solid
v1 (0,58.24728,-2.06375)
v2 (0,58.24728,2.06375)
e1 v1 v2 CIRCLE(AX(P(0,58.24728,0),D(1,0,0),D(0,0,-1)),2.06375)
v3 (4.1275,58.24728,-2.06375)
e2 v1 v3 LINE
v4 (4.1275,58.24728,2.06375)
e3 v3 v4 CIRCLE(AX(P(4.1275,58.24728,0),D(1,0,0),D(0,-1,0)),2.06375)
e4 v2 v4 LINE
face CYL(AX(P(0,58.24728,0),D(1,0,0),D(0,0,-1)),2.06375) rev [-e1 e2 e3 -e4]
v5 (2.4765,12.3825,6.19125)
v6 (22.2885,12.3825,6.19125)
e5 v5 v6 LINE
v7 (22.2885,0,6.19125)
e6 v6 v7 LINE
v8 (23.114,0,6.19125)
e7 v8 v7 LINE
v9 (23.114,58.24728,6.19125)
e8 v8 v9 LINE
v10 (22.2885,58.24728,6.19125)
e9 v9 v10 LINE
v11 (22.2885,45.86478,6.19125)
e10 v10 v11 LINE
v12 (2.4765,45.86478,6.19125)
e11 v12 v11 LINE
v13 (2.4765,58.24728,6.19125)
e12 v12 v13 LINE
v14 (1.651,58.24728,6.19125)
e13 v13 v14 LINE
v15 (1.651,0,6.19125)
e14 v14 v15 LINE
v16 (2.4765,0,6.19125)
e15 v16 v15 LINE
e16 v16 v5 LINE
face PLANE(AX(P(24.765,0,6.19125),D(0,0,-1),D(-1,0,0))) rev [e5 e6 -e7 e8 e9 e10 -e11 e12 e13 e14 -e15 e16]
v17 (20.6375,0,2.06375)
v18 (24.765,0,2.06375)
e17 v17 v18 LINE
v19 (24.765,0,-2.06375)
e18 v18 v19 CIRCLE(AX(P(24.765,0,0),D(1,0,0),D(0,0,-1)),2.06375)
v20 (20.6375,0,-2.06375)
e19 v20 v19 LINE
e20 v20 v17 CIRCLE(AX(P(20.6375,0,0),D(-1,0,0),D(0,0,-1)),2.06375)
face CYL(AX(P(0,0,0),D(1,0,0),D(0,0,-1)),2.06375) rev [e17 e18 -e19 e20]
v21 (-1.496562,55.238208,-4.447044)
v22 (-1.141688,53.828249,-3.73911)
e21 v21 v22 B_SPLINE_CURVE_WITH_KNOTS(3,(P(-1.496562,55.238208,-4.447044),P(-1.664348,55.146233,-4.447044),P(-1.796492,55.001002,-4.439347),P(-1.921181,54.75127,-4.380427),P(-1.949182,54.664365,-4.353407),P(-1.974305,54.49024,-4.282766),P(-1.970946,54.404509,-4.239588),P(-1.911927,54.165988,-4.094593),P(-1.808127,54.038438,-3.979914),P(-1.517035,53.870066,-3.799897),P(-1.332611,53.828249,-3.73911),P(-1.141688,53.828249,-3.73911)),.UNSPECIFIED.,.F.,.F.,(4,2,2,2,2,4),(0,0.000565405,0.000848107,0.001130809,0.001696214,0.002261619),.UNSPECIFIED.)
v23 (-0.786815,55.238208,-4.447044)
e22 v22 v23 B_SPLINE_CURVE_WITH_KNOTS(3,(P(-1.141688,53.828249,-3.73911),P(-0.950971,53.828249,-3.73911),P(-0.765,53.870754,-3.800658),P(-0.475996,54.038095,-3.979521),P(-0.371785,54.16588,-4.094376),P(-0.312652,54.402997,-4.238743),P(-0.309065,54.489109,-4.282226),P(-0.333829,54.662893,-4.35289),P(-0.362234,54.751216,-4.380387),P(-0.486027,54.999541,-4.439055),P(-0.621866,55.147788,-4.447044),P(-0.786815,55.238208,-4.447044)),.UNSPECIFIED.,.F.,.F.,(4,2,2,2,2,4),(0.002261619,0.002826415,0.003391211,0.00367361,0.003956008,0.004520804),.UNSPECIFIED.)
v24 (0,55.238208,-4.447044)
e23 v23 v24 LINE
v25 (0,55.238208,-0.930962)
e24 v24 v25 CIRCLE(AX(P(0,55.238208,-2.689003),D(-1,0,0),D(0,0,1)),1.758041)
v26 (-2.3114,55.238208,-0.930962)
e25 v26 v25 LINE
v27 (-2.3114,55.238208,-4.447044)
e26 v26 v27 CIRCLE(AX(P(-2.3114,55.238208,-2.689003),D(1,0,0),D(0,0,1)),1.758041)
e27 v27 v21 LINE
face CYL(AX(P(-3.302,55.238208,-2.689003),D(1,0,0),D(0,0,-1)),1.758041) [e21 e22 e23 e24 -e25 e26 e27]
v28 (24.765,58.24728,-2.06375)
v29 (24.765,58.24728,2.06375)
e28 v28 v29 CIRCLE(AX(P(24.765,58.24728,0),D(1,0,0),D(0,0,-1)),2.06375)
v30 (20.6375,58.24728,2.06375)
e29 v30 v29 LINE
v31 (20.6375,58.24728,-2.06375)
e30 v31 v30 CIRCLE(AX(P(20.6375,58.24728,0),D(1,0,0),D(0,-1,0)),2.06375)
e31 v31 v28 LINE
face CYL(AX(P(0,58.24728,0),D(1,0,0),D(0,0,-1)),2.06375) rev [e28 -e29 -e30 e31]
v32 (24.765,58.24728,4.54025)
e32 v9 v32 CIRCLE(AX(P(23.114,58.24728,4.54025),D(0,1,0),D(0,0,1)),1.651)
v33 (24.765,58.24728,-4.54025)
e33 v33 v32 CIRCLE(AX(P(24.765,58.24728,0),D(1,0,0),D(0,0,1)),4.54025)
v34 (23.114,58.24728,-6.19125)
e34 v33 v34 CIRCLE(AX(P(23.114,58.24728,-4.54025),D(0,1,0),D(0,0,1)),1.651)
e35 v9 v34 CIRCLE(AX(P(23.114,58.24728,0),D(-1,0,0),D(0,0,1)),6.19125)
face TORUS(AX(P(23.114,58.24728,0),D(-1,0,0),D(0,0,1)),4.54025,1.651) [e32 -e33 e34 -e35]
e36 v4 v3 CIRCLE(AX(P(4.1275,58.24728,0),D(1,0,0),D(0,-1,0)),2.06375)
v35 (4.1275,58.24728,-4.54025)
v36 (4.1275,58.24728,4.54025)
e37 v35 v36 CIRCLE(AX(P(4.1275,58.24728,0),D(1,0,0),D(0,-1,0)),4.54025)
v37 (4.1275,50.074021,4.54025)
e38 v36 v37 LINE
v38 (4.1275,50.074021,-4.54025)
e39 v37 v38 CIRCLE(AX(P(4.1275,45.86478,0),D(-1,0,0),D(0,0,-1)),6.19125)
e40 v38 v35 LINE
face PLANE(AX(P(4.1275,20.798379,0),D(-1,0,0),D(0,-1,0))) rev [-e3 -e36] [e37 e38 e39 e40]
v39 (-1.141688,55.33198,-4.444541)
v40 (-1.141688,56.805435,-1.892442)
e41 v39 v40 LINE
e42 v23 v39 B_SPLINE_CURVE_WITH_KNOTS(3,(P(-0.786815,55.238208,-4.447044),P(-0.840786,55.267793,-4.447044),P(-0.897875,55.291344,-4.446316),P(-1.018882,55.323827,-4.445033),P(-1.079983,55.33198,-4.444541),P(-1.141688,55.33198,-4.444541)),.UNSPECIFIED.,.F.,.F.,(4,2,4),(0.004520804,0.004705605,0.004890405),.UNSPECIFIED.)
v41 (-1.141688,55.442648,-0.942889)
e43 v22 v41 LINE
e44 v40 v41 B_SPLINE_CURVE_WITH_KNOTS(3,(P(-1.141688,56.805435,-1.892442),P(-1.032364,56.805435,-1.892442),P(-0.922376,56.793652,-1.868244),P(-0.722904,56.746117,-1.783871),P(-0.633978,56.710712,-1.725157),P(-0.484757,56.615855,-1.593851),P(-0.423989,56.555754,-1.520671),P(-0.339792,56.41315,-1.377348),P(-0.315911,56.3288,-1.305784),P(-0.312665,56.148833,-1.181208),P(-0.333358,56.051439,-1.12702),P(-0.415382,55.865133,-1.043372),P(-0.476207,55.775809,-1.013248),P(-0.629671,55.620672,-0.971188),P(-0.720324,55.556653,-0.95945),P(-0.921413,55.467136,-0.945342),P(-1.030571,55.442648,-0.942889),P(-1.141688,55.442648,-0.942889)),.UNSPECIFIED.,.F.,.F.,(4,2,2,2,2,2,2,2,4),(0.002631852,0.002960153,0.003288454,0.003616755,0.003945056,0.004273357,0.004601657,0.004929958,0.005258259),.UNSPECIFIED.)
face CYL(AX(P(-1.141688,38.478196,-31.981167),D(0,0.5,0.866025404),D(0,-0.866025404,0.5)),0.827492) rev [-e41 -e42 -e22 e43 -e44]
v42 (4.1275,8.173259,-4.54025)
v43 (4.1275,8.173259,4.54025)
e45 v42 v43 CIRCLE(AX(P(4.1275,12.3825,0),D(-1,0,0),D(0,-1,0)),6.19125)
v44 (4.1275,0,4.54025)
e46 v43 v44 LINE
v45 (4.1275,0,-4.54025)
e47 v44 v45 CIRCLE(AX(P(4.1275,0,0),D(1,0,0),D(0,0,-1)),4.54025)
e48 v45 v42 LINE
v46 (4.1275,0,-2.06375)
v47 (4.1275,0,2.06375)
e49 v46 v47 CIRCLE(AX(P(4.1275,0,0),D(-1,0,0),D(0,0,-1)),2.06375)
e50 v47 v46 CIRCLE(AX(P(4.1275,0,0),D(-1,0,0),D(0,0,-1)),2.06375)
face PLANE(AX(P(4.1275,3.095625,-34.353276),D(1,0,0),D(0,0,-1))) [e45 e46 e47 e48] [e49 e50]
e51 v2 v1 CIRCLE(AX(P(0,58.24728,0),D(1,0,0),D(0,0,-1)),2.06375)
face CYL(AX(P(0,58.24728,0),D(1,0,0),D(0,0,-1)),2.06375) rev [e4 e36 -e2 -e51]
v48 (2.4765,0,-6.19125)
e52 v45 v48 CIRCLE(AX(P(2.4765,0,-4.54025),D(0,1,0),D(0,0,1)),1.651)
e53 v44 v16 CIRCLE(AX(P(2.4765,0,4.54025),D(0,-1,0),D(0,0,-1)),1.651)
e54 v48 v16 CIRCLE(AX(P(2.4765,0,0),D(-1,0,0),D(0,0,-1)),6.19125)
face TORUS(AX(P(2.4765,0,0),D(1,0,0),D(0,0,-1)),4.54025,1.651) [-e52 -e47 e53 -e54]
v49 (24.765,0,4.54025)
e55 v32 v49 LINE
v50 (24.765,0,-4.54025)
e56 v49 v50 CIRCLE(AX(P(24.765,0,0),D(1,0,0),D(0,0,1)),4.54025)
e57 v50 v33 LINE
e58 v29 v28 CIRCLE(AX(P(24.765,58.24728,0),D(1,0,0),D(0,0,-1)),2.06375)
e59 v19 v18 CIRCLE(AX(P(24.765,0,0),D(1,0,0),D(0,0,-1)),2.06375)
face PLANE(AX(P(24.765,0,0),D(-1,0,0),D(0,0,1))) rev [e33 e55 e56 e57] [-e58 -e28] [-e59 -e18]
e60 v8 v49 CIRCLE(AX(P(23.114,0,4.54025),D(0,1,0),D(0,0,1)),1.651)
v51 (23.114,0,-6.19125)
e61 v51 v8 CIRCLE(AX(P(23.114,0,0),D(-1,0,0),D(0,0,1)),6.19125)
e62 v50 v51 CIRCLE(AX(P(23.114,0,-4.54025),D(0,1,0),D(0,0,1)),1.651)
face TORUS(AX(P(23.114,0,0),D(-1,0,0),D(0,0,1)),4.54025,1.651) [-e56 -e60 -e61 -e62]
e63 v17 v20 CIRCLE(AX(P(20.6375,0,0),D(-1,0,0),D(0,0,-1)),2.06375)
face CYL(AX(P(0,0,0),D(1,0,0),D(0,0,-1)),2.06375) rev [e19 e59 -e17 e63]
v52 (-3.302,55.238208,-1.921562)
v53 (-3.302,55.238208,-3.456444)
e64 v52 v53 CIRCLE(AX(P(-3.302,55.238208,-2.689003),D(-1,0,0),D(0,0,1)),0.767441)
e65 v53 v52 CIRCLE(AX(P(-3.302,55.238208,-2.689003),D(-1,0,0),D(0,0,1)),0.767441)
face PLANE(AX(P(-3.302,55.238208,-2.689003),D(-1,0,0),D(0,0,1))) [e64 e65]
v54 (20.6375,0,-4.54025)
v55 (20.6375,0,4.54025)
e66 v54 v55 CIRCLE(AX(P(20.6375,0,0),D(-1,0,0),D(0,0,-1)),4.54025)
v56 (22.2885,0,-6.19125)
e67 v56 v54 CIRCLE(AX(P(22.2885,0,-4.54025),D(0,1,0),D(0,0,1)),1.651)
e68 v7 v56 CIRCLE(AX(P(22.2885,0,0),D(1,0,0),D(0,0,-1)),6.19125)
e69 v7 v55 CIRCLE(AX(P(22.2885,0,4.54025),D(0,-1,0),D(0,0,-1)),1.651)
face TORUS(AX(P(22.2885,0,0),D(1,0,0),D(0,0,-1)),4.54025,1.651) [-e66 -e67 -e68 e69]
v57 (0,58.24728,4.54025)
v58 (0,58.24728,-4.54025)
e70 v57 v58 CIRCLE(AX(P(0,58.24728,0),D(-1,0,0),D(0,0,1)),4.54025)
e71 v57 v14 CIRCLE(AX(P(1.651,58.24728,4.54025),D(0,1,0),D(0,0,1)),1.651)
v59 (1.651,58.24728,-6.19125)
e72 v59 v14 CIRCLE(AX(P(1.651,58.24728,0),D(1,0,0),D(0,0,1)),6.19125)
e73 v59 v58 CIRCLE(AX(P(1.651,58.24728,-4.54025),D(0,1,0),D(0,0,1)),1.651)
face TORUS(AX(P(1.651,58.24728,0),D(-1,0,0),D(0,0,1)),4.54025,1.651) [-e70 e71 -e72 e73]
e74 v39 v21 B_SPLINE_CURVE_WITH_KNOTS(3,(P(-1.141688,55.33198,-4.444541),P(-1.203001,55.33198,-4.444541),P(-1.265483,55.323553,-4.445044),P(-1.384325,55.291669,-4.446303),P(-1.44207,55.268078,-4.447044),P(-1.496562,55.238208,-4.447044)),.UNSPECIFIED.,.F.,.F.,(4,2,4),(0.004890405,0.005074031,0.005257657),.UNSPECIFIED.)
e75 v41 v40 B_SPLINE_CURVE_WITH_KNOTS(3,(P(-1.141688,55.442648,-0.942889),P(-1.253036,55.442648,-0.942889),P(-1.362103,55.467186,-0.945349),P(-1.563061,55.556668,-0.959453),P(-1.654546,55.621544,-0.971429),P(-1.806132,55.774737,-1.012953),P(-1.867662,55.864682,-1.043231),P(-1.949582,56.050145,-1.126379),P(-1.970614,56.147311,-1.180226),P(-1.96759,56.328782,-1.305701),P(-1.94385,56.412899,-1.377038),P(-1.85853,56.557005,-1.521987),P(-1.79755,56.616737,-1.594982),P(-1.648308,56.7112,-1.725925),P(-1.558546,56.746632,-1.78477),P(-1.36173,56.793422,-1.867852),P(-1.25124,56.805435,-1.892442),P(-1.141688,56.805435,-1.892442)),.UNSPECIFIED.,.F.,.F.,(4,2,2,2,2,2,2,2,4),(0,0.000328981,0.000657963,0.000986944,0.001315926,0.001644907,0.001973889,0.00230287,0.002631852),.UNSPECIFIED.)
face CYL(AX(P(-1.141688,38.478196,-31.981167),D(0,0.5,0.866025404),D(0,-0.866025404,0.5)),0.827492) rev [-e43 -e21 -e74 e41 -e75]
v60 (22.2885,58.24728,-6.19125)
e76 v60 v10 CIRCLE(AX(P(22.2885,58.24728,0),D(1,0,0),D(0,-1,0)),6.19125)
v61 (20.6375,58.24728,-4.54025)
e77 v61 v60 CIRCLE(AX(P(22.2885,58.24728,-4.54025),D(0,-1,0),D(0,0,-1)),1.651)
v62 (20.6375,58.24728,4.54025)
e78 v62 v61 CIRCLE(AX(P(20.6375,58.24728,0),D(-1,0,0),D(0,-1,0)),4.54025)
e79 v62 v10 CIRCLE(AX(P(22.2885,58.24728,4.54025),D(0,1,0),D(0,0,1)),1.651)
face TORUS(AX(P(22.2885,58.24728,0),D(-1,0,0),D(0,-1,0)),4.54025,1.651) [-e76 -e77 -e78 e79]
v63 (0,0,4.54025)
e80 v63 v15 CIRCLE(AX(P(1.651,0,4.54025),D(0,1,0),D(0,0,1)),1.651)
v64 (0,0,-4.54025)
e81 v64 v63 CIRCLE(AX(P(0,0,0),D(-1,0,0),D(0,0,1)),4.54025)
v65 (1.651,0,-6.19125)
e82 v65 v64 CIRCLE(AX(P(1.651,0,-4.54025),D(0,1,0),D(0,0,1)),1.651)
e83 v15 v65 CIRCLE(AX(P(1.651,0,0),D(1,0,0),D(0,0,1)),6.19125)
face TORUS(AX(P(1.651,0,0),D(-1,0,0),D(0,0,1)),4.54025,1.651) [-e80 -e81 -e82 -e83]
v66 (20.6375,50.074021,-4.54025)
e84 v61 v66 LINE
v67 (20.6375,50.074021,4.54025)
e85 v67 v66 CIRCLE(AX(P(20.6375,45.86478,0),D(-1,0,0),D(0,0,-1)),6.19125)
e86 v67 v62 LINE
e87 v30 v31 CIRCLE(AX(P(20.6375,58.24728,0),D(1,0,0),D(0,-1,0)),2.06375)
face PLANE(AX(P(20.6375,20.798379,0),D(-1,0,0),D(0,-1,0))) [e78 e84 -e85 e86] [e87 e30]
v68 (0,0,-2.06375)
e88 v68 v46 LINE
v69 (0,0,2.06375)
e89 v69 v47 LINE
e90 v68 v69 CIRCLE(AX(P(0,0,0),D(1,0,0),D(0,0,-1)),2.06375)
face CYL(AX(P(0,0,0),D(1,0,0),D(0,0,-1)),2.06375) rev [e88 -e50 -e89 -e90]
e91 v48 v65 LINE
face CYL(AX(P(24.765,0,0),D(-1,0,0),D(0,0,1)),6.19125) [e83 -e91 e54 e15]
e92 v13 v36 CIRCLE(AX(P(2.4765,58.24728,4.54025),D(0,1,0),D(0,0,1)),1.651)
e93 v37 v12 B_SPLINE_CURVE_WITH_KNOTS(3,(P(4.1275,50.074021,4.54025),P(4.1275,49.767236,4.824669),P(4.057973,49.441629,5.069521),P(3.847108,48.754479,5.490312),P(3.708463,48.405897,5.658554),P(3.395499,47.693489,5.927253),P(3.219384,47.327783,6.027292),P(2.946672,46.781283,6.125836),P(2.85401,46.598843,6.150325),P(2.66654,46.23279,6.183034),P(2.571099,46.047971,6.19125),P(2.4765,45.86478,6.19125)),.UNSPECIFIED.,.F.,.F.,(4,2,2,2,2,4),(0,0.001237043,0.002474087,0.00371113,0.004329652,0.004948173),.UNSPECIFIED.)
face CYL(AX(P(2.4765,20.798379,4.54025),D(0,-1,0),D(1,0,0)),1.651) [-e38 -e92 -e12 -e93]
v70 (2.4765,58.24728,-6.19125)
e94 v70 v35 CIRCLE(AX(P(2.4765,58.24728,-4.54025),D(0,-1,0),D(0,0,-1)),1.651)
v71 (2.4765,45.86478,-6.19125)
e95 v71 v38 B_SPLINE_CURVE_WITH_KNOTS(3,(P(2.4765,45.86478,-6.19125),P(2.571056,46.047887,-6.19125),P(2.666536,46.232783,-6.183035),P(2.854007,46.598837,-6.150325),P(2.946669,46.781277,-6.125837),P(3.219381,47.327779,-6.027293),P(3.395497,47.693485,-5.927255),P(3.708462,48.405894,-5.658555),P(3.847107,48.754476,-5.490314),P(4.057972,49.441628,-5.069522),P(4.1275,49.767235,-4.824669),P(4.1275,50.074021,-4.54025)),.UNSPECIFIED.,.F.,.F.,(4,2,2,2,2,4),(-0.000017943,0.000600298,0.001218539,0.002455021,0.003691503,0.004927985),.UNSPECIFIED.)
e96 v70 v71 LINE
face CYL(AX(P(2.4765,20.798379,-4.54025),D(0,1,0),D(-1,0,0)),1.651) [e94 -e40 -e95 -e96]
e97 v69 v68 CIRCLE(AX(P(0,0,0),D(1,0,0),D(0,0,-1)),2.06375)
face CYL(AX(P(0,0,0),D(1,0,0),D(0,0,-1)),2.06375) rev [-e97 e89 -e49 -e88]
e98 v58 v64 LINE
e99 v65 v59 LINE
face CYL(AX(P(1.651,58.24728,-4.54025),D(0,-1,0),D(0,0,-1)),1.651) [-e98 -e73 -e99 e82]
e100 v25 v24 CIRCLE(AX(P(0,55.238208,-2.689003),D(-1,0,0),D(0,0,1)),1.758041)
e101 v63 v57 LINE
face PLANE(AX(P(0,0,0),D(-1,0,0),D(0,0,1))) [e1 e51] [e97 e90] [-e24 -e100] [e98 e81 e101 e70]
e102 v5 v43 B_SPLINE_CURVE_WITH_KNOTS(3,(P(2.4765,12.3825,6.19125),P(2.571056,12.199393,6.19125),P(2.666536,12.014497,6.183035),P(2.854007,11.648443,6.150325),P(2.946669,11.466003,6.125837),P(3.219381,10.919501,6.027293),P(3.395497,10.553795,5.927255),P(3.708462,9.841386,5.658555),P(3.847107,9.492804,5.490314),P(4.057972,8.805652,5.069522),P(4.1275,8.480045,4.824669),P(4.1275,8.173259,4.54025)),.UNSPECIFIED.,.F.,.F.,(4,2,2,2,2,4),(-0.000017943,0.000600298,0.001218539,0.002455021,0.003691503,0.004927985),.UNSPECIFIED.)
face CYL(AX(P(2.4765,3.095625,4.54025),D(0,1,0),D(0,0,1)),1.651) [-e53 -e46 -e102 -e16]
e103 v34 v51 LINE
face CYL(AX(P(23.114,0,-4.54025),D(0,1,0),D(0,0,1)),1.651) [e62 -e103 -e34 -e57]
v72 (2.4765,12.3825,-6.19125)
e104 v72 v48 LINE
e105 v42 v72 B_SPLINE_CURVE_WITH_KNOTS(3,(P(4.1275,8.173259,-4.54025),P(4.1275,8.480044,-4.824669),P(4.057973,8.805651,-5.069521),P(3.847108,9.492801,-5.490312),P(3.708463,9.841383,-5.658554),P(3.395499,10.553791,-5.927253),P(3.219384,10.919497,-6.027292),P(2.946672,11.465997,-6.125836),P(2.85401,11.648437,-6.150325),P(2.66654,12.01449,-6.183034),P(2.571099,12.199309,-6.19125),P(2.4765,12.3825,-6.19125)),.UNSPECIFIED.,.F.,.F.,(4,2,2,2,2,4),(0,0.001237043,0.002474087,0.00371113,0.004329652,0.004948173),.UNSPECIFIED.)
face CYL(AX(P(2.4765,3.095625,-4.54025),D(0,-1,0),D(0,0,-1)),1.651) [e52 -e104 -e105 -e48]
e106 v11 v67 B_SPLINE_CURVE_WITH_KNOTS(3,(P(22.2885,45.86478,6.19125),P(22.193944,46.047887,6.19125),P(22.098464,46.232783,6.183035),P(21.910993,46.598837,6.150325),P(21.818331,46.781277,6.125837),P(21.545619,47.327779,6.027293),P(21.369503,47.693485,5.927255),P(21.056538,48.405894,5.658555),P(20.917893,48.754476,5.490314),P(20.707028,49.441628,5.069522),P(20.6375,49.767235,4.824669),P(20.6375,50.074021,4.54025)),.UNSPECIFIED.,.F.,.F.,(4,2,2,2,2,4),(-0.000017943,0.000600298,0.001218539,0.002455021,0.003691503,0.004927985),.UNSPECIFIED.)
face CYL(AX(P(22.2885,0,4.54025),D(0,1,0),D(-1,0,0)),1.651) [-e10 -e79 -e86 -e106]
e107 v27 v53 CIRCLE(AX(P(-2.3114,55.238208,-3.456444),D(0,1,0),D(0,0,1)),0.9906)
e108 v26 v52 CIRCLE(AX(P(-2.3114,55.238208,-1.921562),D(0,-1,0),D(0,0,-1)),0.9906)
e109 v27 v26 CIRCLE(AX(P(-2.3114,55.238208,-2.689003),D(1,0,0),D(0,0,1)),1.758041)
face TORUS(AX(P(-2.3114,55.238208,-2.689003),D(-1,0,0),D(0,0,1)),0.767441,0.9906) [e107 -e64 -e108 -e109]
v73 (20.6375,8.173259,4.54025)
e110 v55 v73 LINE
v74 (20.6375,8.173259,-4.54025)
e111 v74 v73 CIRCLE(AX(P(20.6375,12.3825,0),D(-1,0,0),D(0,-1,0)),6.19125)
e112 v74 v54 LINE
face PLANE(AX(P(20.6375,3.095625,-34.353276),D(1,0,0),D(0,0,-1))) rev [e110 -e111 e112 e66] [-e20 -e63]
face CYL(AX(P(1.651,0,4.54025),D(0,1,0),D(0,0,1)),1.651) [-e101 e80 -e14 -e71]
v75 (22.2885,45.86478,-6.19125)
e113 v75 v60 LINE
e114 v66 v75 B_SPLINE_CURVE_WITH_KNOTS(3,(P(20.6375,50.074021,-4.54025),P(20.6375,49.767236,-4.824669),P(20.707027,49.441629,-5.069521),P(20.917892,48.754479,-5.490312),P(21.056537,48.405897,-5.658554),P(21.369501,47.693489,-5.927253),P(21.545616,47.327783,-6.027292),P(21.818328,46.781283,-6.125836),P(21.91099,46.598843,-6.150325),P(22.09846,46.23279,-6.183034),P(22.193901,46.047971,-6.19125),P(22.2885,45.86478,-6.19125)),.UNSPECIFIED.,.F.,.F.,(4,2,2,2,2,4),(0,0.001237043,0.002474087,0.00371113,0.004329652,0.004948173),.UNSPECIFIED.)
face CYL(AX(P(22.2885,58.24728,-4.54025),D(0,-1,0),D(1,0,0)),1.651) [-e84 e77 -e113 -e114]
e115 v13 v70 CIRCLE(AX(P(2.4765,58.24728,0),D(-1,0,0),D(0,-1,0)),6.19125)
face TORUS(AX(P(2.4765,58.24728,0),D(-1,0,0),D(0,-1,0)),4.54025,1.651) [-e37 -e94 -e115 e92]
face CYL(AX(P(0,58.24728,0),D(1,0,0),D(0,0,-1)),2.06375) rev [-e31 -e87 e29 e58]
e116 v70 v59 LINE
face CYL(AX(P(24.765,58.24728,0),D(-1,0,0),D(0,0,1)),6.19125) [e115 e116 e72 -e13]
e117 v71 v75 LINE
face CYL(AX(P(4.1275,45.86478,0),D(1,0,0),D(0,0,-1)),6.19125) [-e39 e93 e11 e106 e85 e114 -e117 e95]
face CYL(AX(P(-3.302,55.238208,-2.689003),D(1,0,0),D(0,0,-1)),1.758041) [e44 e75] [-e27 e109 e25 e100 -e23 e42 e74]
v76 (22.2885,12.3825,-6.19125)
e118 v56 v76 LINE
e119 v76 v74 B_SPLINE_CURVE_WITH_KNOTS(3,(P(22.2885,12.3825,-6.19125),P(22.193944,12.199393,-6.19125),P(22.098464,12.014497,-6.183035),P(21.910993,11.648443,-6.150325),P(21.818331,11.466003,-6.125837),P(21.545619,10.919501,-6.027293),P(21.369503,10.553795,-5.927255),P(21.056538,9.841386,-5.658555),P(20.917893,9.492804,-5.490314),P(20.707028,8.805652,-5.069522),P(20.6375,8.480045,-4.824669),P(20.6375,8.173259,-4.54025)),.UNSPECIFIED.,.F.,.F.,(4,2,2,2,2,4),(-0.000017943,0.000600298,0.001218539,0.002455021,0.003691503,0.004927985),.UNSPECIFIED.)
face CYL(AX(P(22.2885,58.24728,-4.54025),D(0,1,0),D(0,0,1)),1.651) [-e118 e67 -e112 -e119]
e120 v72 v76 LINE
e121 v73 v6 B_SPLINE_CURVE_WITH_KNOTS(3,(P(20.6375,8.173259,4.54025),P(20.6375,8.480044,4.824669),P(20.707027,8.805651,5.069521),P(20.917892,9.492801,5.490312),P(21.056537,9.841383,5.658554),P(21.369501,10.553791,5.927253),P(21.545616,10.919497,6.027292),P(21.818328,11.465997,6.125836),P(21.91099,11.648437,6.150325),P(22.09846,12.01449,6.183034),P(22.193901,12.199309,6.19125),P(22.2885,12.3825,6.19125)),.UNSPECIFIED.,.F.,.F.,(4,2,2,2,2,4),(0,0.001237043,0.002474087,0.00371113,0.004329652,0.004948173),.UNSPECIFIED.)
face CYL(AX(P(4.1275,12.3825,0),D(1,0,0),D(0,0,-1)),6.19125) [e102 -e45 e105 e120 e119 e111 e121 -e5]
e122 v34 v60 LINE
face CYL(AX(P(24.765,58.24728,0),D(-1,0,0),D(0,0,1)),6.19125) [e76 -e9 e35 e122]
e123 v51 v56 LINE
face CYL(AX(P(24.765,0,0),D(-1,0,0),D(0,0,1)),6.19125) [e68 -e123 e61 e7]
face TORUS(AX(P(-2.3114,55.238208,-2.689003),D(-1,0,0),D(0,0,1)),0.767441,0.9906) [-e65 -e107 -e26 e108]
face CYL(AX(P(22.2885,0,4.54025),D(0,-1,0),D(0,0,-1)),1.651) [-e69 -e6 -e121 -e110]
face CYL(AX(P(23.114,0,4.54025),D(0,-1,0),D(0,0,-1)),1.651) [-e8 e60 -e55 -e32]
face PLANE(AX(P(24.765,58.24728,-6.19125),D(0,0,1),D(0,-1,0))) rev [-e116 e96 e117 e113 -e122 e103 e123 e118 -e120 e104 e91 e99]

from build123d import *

# Parameters (mm, degrees)
BOSS_EXTRUDE1_DEPTH = 19.05
SKETCH2_R           = 1.5875
SKETCH2_R_2         = 1.5874999999999988
CUT_EXTRUDE1_DEPTH  = 19.05
CUT_EXTRUDE2_DEPTH  = 6.35
FILLET1_R           = 1.27
SKETCH3_R           = 1.3523393116529026
BOSS_EXTRUDE2_DEPTH = 2.54
FILLET2_R           = 0.762
SKETCH4_R           = 0.6365323226185287
CUT_EXTRUDE3_DEPTH  = 50.150613196033525
SCALE_RATIO_1_SCALE = 1.3


with BuildPart() as part:
    # Sketch1 → Boss-Extrude1 (new body)
    with BuildSketch(Plane(origin=(0, 0, 0), x_dir=(0, 0, -1), z_dir=(1, 0, 0))):
        with BuildLine():
            Line((-4.7625, 0), (-4.7625, 44.8056))
            ThreePointArc((-4.7625, 44.8056), (2.9e-16, 49.5681), (4.7625, 44.8056))
            Line((4.7625, 44.8056), (4.762500000000005, 5.8e-16))
            ThreePointArc((4.762500000000005, 5.8e-16), (1.35e-15, -4.762500000000005), (-4.7625, 0))
        make_face()
    extrude(amount=BOSS_EXTRUDE1_DEPTH)

    # Sketch2 → Cut-Extrude1 (cut)
    with BuildSketch(Plane(origin=(19.05, 0, 0), x_dir=(0, 0, -1), z_dir=(1, 0, 0))):
        Circle(SKETCH2_R)
        with Locations((0, 44.8056)):
            Circle(SKETCH2_R_2)
    extrude(amount=-CUT_EXTRUDE1_DEPTH, mode=Mode.SUBTRACT)

    # 3DSketch1 → Cut-Extrude2 (cut, symmetric)
    with BuildSketch(Plane(origin=(9.524999999999954, 44.80559999999997, -4.762500000000004), x_dir=(0, -0.9781419365644765, 0.20793833685469326), z_dir=(-1, -9.3e-16, 3.6e-16))):
        with BuildLine():
            Line((0, 0), (9.316801945776646, -1.9806126585409503))
            ThreePointArc((9.316801945776646, -1.9806126585409503), (5.6487073021588, 3.668094643617845), (11.2974146043176, 7.336189287235693))
            Line((11.2974146043176, 7.336189287235693), (1.9806126585409412, 9.316801945776648))
            ThreePointArc((1.9806126585409412, 9.316801945776648), (-3.6680946436178474, 5.648707302158794), (0, 0))
        make_face()
        with BuildLine():
            Line((45.806849011474235, 0), (36.49004706569759, 1.980612658540955))
            ThreePointArc((36.49004706569759, 1.980612658540955), (40.15814170931544, -3.668094643617836), (34.50943440715664, -7.336189287235687))
            Line((34.50943440715664, -7.336189287235687), (43.82623635293327, -9.316801945776637))
            ThreePointArc((43.82623635293327, -9.316801945776637), (49.47494365509206, -5.648707302158793), (45.806849011474235, 0))
        make_face()
    extrude(amount=CUT_EXTRUDE2_DEPTH, both=True, mode=Mode.SUBTRACT)

    # Fillet1
    fillet1_edges = [part.edges().sort_by_distance(p)[0] for p in [
        (19.05, 49.5681, 7e-17),
        (19.05, 22.4028, 4.7625),
        (15.874999999999961, 40.04309999999998, 4.762500000000003),
        (15.874999999999957, 40.043099999999974, -4.762500000000005),
        (3.174999999999959, 40.04309999999996, -4.762499999999999),
        (3.1749999999999625, 40.04309999999997, 4.762500000000008),
        (19.05, -4.762500000000005, -2.98e-15),
        (0, 22.4028, 4.7625),
        (0, 49.5681, 7e-17),
        (15.874999999999995, 4.762500000000003, 4.762499999999996),
        (15.874999999999991, 4.762500000000003, -4.762500000000006),
        (3.1749999999999954, 4.762499999999989, 4.762500000000001),
        (3.174999999999992, 4.762499999999989, -4.762500000000001),
        (0, 22.4028, -4.762500000000003),
        (0, -4.762500000000005, -2.98e-15),
        (19.05, 22.4028, -4.762500000000003),
    ]]
    fillet(fillet1_edges, radius=FILLET1_R)

    # Sketch3 → Boss-Extrude2 (add)
    with BuildSketch(Plane.ZY):
        with Locations((-2.068463746823568, 42.49092897757123)):
            Circle(SKETCH3_R)
    extrude(amount=BOSS_EXTRUDE2_DEPTH)

    # Fillet2
    fillet2_edges = [part.edges().sort_by_distance(p)[0] for p in [
        (-2.54, 42.49092897757123, -3.42080305847647),
    ]]
    fillet(fillet2_edges, radius=FILLET2_R)

    # Sketch4 → Cut-Extrude3 (cut, through all)
    with BuildSketch(Plane(origin=(0, 10.403230824440865, 18.01892435079848), x_dir=(-1, 0, 0), z_dir=(0, 0.49999999999999484, 0.8660254037844416))):
        with Locations(Location((0.8782218587697344, -37.93359892462922, 0), (0, 0, 90))):
            Circle(SKETCH4_R)
    extrude(amount=-CUT_EXTRUDE3_DEPTH, mode=Mode.SUBTRACT)


with BuildPart() as part_1:
    # Scale ratio 1: scaled about (0, 0, 0)
    add(part.part.scale(SCALE_RATIO_1_SCALE))


solid = part_1.part
